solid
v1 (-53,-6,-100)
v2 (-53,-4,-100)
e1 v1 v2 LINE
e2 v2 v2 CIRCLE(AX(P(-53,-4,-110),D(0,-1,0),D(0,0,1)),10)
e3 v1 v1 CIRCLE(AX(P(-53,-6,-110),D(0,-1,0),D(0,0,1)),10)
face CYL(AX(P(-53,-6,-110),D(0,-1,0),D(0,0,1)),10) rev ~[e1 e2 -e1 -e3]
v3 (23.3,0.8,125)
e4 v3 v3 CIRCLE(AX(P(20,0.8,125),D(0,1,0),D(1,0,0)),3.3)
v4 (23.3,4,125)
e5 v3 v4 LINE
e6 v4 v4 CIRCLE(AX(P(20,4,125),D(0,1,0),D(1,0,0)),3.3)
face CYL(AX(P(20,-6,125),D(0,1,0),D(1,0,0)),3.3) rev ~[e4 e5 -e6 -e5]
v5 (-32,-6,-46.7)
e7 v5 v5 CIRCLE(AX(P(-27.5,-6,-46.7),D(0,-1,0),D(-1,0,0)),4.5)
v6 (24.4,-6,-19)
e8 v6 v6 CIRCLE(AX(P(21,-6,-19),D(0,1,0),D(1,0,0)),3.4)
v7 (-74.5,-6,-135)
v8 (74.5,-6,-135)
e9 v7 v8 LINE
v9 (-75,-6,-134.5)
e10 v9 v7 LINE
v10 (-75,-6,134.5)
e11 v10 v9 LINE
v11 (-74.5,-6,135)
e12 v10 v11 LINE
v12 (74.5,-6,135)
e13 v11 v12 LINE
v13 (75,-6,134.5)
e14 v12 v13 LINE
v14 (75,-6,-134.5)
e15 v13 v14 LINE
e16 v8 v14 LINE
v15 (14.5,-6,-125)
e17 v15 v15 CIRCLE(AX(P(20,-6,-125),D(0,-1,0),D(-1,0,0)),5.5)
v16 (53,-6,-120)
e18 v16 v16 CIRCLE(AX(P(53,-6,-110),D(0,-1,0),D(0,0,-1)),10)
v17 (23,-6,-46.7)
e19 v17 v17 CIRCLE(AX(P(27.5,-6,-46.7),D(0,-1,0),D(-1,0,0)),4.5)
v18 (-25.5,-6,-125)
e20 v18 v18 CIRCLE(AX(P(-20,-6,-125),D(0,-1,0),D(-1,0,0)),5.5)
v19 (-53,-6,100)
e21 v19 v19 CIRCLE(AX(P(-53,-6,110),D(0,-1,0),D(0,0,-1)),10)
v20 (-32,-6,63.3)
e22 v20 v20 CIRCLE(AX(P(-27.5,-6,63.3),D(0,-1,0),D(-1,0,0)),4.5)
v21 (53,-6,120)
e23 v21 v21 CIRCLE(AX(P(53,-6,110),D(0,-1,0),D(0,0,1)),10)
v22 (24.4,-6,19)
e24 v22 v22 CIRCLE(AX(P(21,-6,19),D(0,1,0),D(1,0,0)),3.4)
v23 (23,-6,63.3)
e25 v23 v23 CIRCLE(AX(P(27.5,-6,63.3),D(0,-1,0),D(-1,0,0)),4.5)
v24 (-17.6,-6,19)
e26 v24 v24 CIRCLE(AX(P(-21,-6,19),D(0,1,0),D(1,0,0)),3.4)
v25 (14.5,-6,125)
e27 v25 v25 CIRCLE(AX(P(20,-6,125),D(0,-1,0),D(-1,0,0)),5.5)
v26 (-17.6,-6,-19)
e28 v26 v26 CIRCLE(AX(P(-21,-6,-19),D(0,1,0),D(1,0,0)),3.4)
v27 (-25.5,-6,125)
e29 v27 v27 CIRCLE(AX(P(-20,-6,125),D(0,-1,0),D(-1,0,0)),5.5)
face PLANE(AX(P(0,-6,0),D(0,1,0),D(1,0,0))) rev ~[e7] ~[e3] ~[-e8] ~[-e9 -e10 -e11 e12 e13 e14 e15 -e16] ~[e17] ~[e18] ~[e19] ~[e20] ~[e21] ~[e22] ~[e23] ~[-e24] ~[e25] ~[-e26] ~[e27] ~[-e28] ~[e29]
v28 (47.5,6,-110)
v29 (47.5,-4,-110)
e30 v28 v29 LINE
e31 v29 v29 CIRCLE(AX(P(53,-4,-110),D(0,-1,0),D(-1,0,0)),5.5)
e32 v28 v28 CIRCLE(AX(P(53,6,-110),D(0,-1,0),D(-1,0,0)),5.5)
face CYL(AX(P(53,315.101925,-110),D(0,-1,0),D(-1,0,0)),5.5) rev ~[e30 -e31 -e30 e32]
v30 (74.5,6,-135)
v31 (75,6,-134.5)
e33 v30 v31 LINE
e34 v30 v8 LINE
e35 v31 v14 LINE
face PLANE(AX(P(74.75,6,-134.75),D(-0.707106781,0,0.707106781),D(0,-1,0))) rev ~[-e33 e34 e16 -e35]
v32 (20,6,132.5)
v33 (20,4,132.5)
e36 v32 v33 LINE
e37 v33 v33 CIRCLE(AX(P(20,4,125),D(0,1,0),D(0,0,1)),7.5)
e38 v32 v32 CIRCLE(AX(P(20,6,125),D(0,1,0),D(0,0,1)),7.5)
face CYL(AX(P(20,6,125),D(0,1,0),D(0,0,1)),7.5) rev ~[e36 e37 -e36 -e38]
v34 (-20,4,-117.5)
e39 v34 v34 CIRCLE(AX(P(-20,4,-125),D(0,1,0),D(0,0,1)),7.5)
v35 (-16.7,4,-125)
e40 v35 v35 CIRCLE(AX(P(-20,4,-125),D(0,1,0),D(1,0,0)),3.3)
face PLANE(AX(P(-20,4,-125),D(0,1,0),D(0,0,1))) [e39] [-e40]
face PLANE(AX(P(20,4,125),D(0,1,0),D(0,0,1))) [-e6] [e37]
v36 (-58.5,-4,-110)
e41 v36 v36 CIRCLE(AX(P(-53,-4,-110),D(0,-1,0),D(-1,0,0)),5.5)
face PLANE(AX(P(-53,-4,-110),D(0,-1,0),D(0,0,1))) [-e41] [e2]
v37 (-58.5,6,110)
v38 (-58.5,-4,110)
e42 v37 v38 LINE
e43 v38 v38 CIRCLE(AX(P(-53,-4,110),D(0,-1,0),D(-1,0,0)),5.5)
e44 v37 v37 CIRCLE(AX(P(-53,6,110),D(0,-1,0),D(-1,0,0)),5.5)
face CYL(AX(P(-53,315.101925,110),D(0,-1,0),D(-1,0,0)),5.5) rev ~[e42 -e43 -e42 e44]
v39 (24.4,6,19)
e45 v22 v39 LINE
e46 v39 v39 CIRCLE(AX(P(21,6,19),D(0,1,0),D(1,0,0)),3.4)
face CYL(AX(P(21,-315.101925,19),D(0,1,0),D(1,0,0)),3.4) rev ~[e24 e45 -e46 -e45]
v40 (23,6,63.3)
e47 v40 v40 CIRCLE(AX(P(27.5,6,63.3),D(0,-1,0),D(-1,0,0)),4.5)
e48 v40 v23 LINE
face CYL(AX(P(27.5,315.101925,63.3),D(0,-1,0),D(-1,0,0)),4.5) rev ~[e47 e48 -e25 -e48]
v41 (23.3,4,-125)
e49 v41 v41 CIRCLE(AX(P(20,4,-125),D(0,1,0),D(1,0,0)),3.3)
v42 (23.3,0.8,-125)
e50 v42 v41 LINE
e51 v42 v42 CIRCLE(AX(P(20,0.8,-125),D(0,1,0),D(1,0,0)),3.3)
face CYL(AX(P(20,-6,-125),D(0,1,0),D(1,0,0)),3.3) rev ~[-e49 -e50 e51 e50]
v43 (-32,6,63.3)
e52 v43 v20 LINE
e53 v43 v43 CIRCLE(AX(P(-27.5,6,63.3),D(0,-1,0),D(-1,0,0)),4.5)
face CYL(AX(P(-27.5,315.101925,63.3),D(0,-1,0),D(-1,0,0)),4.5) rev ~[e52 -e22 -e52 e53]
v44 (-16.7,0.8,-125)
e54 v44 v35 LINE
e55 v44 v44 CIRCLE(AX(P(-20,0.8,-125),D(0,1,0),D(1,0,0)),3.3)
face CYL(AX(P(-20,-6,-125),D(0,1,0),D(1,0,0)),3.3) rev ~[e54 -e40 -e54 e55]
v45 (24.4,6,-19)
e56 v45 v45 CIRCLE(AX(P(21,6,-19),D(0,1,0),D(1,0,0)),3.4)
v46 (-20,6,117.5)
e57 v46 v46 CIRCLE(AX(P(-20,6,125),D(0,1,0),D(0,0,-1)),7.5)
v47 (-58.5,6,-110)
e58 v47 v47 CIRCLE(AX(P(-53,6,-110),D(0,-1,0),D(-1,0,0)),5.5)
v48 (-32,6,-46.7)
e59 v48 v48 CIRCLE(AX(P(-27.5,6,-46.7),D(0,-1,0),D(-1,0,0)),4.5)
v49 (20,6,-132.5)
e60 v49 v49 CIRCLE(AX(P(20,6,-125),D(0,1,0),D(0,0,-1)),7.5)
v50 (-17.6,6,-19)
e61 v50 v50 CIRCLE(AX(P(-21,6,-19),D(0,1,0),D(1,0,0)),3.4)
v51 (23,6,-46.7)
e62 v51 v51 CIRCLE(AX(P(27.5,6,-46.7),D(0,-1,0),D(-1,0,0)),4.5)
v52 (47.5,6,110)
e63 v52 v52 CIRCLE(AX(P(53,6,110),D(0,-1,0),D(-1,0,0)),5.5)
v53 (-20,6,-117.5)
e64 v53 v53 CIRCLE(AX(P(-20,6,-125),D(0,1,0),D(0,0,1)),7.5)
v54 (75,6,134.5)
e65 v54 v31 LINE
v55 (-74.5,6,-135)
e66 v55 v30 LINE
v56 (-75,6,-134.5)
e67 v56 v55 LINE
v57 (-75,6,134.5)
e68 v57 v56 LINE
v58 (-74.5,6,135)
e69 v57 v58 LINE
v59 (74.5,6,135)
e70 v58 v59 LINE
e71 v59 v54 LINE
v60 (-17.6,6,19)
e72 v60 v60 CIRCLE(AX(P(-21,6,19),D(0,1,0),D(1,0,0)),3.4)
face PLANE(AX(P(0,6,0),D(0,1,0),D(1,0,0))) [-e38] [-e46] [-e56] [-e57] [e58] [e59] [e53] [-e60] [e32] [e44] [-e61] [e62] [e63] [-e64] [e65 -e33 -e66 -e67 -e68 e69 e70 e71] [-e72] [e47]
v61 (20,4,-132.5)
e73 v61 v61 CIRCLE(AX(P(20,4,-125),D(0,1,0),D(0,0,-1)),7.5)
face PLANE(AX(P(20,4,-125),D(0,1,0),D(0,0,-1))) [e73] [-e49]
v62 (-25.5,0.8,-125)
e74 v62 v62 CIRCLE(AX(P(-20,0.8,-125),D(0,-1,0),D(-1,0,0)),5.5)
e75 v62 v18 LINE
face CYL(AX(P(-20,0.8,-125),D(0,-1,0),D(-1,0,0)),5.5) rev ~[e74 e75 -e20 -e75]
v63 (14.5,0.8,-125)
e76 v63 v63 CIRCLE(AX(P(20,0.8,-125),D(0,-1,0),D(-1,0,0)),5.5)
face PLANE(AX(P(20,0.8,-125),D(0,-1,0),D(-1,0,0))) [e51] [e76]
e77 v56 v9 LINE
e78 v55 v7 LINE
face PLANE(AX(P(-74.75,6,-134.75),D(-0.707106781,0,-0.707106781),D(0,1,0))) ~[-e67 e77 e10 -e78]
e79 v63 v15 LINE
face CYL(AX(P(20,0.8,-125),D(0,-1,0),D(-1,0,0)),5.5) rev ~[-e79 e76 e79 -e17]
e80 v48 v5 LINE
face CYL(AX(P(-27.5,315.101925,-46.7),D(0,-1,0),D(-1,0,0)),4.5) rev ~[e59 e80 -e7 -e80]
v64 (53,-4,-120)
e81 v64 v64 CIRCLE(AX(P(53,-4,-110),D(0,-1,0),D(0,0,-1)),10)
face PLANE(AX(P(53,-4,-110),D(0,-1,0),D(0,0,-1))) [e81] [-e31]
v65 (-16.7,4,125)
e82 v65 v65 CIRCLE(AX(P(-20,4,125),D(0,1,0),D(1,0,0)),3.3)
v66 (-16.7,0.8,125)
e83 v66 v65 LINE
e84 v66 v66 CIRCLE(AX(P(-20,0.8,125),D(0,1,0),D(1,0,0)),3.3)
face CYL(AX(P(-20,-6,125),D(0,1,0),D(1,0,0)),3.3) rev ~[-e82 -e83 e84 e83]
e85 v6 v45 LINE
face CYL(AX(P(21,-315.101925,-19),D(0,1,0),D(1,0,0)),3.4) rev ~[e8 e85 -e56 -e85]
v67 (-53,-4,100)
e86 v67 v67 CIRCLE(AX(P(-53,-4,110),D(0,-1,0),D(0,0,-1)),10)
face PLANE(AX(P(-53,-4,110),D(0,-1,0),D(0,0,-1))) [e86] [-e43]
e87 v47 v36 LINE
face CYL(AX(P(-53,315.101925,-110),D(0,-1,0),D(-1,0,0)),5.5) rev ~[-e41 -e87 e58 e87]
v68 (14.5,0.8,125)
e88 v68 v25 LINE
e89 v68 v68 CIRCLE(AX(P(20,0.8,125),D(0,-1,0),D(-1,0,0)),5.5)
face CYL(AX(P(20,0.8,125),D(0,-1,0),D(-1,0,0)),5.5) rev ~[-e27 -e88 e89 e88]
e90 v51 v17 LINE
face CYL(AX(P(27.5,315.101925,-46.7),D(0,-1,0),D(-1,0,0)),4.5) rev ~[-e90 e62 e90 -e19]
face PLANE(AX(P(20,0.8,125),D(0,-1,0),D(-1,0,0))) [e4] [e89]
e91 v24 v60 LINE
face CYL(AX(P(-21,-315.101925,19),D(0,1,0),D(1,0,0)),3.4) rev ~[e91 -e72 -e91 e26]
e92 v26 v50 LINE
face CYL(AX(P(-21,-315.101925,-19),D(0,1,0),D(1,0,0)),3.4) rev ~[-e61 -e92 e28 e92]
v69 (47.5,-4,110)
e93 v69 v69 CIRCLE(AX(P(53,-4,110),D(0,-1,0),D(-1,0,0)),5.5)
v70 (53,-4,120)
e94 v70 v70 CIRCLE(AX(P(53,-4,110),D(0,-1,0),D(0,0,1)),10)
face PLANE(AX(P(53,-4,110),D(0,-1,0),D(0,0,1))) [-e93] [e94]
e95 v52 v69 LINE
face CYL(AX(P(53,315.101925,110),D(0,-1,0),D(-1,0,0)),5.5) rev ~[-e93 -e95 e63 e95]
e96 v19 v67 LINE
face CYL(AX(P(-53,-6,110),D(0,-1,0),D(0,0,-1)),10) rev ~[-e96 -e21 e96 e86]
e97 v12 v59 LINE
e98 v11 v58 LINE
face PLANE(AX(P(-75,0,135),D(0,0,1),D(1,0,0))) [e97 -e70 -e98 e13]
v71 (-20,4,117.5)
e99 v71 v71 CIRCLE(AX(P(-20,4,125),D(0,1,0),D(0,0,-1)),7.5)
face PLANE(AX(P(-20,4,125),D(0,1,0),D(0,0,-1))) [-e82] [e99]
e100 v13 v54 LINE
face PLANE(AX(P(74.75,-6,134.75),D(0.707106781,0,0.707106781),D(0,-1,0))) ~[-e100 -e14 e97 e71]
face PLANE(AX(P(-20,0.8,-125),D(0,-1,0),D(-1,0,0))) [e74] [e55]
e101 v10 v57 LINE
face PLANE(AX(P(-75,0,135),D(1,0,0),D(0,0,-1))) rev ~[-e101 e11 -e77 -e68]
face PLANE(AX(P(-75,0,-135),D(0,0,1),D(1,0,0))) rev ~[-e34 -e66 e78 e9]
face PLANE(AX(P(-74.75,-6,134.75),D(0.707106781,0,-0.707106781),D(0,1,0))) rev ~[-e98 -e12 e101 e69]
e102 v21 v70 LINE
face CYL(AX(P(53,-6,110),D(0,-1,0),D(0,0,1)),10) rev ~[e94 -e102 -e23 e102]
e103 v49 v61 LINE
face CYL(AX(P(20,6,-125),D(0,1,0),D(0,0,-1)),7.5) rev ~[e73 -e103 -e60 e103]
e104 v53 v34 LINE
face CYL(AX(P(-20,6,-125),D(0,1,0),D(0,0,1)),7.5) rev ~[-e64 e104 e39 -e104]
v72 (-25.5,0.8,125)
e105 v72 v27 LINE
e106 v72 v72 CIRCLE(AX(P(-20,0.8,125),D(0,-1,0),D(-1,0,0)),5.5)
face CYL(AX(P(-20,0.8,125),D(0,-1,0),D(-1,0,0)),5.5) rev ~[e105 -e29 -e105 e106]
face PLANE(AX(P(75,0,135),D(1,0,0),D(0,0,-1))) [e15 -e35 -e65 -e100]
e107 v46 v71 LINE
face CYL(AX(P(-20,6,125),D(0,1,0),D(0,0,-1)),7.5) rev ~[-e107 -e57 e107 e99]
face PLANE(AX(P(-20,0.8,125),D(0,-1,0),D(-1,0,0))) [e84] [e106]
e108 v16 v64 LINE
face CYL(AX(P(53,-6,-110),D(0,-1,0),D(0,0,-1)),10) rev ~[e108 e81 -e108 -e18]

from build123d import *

# Parameters (mm, degrees)
SKETCH1_W                                            = 150
SKETCH1_H                                            = 270
BOSS_EXTRUDE1_DEPTH                                  = 6
SKETCH2_R                                            = 10
CUT_EXTRUDE1_DEPTH                                   = 2
M10_CLEARANCE_HOLE1_D                                = 11
SKETCH5_R                                            = 7.5
CUT_EXTRUDE2_DEPTH                                   = 2
HOLE_SIZE_PER_SOCKET_HEAD_CAP_SCREW_TYPE_D           = 6.6
HOLE_SIZE_PER_SOCKET_HEAD_CAP_SCREW_TYPE_CBORE_D     = 11
HOLE_SIZE_PER_SOCKET_HEAD_CAP_SCREW_TYPE_CBORE_DEPTH = 6.8
M8_TAPPED_HOLE2_D                                    = 6.8
CHAMFER1_SIZE                                        = 0.5
M8_CLEARANCE_HOLE1_D                                 = 9


with BuildPart() as part:
    # Sketch1 → Boss-Extrude1 (new, symmetric)
    with BuildSketch(Plane(origin=(0, 0, 0), x_dir=(1, 0, 0), z_dir=(0, 1, 0))):
        Rectangle(SKETCH1_W, SKETCH1_H)
    extrude(amount=BOSS_EXTRUDE1_DEPTH, both=True)

    # Sketch2 → Cut-Extrude1 (cut)
    with BuildSketch(Plane.XZ.offset(6)):
        with Locations(Location((-53, 110, 0), (0, 0, 270))):
            Circle(SKETCH2_R)
        with Locations(Location((53, 110, 0), (0, 0, 90))):
            Circle(SKETCH2_R)
        with Locations(Location((53, -110, 0), (0, 0, 270))):
            Circle(SKETCH2_R)
        with Locations(Location((-53, -110, 0), (0, 0, 90))):
            Circle(SKETCH2_R)
    extrude(amount=-CUT_EXTRUDE1_DEPTH, mode=Mode.SUBTRACT)

    # M10 Clearance Hole1 (through all)
    with Locations(Plane(origin=(0, 6, 0), x_dir=(1, 0, 0), z_dir=(0, 1, 0))):
        with Locations((-53, 110), (53, 110), (-53, -110), (53, -110)):
            Hole(M10_CLEARANCE_HOLE1_D / 2)

    # Sketch5 → Cut-Extrude2 (cut)
    with BuildSketch(Plane(origin=(0, 6, 0), x_dir=(1, 0, 0), z_dir=(0, 1, 0))):
        with Locations(Location((-20, 125, 0), (0, 0, 270))):
            Circle(SKETCH5_R)
        with Locations(Location((20, 125, 0), (0, 0, 90))):
            Circle(SKETCH5_R)
        with Locations(Location((20, -125, 0), (0, 0, 270))):
            Circle(SKETCH5_R)
        with Locations(Location((-20, -125, 0), (0, 0, 90))):
            Circle(SKETCH5_R)
    extrude(amount=-CUT_EXTRUDE2_DEPTH, mode=Mode.SUBTRACT)

    # Hole size per socket head cap screw type 1 (through all)
    with Locations(Plane(origin=(0, -6, 0), x_dir=(-1, 0, 0), z_dir=(0, -1, 0))):
        with Locations((20, -125), (-20, -125), (20, 125), (-20, 125)):
            CounterBoreHole(HOLE_SIZE_PER_SOCKET_HEAD_CAP_SCREW_TYPE_D / 2, HOLE_SIZE_PER_SOCKET_HEAD_CAP_SCREW_TYPE_CBORE_D / 2, HOLE_SIZE_PER_SOCKET_HEAD_CAP_SCREW_TYPE_CBORE_DEPTH)

    # M8 Tapped Hole2 (through all)
    with Locations(Plane(origin=(0, -6, 0), x_dir=(-1, 0, 0), z_dir=(0, -1, 0))):
        with Locations((21, 19), (21, -19), (-21, -19), (-21, 19)):
            Hole(M8_TAPPED_HOLE2_D / 2)

    # Chamfer1
    chamfer1_edges = [part.edges().sort_by_distance(p)[0] for p in [
        (75, 0, 135),
        (-75, 0, 135),
        (-75, 0, -135),
        (75, 0, -135),
    ]]
    chamfer(chamfer1_edges, length=CHAMFER1_SIZE)

    # M8 Clearance Hole1 (through all)
    with Locations(Plane(origin=(0, 6, 0), x_dir=(1, 0, 0), z_dir=(0, 1, 0))):
        with Locations((27.5, 46.7), (-27.5, 46.7), (27.5, -63.3), (-27.5, -63.3)):
            Hole(M8_CLEARANCE_HOLE1_D / 2)


solid = part.part
